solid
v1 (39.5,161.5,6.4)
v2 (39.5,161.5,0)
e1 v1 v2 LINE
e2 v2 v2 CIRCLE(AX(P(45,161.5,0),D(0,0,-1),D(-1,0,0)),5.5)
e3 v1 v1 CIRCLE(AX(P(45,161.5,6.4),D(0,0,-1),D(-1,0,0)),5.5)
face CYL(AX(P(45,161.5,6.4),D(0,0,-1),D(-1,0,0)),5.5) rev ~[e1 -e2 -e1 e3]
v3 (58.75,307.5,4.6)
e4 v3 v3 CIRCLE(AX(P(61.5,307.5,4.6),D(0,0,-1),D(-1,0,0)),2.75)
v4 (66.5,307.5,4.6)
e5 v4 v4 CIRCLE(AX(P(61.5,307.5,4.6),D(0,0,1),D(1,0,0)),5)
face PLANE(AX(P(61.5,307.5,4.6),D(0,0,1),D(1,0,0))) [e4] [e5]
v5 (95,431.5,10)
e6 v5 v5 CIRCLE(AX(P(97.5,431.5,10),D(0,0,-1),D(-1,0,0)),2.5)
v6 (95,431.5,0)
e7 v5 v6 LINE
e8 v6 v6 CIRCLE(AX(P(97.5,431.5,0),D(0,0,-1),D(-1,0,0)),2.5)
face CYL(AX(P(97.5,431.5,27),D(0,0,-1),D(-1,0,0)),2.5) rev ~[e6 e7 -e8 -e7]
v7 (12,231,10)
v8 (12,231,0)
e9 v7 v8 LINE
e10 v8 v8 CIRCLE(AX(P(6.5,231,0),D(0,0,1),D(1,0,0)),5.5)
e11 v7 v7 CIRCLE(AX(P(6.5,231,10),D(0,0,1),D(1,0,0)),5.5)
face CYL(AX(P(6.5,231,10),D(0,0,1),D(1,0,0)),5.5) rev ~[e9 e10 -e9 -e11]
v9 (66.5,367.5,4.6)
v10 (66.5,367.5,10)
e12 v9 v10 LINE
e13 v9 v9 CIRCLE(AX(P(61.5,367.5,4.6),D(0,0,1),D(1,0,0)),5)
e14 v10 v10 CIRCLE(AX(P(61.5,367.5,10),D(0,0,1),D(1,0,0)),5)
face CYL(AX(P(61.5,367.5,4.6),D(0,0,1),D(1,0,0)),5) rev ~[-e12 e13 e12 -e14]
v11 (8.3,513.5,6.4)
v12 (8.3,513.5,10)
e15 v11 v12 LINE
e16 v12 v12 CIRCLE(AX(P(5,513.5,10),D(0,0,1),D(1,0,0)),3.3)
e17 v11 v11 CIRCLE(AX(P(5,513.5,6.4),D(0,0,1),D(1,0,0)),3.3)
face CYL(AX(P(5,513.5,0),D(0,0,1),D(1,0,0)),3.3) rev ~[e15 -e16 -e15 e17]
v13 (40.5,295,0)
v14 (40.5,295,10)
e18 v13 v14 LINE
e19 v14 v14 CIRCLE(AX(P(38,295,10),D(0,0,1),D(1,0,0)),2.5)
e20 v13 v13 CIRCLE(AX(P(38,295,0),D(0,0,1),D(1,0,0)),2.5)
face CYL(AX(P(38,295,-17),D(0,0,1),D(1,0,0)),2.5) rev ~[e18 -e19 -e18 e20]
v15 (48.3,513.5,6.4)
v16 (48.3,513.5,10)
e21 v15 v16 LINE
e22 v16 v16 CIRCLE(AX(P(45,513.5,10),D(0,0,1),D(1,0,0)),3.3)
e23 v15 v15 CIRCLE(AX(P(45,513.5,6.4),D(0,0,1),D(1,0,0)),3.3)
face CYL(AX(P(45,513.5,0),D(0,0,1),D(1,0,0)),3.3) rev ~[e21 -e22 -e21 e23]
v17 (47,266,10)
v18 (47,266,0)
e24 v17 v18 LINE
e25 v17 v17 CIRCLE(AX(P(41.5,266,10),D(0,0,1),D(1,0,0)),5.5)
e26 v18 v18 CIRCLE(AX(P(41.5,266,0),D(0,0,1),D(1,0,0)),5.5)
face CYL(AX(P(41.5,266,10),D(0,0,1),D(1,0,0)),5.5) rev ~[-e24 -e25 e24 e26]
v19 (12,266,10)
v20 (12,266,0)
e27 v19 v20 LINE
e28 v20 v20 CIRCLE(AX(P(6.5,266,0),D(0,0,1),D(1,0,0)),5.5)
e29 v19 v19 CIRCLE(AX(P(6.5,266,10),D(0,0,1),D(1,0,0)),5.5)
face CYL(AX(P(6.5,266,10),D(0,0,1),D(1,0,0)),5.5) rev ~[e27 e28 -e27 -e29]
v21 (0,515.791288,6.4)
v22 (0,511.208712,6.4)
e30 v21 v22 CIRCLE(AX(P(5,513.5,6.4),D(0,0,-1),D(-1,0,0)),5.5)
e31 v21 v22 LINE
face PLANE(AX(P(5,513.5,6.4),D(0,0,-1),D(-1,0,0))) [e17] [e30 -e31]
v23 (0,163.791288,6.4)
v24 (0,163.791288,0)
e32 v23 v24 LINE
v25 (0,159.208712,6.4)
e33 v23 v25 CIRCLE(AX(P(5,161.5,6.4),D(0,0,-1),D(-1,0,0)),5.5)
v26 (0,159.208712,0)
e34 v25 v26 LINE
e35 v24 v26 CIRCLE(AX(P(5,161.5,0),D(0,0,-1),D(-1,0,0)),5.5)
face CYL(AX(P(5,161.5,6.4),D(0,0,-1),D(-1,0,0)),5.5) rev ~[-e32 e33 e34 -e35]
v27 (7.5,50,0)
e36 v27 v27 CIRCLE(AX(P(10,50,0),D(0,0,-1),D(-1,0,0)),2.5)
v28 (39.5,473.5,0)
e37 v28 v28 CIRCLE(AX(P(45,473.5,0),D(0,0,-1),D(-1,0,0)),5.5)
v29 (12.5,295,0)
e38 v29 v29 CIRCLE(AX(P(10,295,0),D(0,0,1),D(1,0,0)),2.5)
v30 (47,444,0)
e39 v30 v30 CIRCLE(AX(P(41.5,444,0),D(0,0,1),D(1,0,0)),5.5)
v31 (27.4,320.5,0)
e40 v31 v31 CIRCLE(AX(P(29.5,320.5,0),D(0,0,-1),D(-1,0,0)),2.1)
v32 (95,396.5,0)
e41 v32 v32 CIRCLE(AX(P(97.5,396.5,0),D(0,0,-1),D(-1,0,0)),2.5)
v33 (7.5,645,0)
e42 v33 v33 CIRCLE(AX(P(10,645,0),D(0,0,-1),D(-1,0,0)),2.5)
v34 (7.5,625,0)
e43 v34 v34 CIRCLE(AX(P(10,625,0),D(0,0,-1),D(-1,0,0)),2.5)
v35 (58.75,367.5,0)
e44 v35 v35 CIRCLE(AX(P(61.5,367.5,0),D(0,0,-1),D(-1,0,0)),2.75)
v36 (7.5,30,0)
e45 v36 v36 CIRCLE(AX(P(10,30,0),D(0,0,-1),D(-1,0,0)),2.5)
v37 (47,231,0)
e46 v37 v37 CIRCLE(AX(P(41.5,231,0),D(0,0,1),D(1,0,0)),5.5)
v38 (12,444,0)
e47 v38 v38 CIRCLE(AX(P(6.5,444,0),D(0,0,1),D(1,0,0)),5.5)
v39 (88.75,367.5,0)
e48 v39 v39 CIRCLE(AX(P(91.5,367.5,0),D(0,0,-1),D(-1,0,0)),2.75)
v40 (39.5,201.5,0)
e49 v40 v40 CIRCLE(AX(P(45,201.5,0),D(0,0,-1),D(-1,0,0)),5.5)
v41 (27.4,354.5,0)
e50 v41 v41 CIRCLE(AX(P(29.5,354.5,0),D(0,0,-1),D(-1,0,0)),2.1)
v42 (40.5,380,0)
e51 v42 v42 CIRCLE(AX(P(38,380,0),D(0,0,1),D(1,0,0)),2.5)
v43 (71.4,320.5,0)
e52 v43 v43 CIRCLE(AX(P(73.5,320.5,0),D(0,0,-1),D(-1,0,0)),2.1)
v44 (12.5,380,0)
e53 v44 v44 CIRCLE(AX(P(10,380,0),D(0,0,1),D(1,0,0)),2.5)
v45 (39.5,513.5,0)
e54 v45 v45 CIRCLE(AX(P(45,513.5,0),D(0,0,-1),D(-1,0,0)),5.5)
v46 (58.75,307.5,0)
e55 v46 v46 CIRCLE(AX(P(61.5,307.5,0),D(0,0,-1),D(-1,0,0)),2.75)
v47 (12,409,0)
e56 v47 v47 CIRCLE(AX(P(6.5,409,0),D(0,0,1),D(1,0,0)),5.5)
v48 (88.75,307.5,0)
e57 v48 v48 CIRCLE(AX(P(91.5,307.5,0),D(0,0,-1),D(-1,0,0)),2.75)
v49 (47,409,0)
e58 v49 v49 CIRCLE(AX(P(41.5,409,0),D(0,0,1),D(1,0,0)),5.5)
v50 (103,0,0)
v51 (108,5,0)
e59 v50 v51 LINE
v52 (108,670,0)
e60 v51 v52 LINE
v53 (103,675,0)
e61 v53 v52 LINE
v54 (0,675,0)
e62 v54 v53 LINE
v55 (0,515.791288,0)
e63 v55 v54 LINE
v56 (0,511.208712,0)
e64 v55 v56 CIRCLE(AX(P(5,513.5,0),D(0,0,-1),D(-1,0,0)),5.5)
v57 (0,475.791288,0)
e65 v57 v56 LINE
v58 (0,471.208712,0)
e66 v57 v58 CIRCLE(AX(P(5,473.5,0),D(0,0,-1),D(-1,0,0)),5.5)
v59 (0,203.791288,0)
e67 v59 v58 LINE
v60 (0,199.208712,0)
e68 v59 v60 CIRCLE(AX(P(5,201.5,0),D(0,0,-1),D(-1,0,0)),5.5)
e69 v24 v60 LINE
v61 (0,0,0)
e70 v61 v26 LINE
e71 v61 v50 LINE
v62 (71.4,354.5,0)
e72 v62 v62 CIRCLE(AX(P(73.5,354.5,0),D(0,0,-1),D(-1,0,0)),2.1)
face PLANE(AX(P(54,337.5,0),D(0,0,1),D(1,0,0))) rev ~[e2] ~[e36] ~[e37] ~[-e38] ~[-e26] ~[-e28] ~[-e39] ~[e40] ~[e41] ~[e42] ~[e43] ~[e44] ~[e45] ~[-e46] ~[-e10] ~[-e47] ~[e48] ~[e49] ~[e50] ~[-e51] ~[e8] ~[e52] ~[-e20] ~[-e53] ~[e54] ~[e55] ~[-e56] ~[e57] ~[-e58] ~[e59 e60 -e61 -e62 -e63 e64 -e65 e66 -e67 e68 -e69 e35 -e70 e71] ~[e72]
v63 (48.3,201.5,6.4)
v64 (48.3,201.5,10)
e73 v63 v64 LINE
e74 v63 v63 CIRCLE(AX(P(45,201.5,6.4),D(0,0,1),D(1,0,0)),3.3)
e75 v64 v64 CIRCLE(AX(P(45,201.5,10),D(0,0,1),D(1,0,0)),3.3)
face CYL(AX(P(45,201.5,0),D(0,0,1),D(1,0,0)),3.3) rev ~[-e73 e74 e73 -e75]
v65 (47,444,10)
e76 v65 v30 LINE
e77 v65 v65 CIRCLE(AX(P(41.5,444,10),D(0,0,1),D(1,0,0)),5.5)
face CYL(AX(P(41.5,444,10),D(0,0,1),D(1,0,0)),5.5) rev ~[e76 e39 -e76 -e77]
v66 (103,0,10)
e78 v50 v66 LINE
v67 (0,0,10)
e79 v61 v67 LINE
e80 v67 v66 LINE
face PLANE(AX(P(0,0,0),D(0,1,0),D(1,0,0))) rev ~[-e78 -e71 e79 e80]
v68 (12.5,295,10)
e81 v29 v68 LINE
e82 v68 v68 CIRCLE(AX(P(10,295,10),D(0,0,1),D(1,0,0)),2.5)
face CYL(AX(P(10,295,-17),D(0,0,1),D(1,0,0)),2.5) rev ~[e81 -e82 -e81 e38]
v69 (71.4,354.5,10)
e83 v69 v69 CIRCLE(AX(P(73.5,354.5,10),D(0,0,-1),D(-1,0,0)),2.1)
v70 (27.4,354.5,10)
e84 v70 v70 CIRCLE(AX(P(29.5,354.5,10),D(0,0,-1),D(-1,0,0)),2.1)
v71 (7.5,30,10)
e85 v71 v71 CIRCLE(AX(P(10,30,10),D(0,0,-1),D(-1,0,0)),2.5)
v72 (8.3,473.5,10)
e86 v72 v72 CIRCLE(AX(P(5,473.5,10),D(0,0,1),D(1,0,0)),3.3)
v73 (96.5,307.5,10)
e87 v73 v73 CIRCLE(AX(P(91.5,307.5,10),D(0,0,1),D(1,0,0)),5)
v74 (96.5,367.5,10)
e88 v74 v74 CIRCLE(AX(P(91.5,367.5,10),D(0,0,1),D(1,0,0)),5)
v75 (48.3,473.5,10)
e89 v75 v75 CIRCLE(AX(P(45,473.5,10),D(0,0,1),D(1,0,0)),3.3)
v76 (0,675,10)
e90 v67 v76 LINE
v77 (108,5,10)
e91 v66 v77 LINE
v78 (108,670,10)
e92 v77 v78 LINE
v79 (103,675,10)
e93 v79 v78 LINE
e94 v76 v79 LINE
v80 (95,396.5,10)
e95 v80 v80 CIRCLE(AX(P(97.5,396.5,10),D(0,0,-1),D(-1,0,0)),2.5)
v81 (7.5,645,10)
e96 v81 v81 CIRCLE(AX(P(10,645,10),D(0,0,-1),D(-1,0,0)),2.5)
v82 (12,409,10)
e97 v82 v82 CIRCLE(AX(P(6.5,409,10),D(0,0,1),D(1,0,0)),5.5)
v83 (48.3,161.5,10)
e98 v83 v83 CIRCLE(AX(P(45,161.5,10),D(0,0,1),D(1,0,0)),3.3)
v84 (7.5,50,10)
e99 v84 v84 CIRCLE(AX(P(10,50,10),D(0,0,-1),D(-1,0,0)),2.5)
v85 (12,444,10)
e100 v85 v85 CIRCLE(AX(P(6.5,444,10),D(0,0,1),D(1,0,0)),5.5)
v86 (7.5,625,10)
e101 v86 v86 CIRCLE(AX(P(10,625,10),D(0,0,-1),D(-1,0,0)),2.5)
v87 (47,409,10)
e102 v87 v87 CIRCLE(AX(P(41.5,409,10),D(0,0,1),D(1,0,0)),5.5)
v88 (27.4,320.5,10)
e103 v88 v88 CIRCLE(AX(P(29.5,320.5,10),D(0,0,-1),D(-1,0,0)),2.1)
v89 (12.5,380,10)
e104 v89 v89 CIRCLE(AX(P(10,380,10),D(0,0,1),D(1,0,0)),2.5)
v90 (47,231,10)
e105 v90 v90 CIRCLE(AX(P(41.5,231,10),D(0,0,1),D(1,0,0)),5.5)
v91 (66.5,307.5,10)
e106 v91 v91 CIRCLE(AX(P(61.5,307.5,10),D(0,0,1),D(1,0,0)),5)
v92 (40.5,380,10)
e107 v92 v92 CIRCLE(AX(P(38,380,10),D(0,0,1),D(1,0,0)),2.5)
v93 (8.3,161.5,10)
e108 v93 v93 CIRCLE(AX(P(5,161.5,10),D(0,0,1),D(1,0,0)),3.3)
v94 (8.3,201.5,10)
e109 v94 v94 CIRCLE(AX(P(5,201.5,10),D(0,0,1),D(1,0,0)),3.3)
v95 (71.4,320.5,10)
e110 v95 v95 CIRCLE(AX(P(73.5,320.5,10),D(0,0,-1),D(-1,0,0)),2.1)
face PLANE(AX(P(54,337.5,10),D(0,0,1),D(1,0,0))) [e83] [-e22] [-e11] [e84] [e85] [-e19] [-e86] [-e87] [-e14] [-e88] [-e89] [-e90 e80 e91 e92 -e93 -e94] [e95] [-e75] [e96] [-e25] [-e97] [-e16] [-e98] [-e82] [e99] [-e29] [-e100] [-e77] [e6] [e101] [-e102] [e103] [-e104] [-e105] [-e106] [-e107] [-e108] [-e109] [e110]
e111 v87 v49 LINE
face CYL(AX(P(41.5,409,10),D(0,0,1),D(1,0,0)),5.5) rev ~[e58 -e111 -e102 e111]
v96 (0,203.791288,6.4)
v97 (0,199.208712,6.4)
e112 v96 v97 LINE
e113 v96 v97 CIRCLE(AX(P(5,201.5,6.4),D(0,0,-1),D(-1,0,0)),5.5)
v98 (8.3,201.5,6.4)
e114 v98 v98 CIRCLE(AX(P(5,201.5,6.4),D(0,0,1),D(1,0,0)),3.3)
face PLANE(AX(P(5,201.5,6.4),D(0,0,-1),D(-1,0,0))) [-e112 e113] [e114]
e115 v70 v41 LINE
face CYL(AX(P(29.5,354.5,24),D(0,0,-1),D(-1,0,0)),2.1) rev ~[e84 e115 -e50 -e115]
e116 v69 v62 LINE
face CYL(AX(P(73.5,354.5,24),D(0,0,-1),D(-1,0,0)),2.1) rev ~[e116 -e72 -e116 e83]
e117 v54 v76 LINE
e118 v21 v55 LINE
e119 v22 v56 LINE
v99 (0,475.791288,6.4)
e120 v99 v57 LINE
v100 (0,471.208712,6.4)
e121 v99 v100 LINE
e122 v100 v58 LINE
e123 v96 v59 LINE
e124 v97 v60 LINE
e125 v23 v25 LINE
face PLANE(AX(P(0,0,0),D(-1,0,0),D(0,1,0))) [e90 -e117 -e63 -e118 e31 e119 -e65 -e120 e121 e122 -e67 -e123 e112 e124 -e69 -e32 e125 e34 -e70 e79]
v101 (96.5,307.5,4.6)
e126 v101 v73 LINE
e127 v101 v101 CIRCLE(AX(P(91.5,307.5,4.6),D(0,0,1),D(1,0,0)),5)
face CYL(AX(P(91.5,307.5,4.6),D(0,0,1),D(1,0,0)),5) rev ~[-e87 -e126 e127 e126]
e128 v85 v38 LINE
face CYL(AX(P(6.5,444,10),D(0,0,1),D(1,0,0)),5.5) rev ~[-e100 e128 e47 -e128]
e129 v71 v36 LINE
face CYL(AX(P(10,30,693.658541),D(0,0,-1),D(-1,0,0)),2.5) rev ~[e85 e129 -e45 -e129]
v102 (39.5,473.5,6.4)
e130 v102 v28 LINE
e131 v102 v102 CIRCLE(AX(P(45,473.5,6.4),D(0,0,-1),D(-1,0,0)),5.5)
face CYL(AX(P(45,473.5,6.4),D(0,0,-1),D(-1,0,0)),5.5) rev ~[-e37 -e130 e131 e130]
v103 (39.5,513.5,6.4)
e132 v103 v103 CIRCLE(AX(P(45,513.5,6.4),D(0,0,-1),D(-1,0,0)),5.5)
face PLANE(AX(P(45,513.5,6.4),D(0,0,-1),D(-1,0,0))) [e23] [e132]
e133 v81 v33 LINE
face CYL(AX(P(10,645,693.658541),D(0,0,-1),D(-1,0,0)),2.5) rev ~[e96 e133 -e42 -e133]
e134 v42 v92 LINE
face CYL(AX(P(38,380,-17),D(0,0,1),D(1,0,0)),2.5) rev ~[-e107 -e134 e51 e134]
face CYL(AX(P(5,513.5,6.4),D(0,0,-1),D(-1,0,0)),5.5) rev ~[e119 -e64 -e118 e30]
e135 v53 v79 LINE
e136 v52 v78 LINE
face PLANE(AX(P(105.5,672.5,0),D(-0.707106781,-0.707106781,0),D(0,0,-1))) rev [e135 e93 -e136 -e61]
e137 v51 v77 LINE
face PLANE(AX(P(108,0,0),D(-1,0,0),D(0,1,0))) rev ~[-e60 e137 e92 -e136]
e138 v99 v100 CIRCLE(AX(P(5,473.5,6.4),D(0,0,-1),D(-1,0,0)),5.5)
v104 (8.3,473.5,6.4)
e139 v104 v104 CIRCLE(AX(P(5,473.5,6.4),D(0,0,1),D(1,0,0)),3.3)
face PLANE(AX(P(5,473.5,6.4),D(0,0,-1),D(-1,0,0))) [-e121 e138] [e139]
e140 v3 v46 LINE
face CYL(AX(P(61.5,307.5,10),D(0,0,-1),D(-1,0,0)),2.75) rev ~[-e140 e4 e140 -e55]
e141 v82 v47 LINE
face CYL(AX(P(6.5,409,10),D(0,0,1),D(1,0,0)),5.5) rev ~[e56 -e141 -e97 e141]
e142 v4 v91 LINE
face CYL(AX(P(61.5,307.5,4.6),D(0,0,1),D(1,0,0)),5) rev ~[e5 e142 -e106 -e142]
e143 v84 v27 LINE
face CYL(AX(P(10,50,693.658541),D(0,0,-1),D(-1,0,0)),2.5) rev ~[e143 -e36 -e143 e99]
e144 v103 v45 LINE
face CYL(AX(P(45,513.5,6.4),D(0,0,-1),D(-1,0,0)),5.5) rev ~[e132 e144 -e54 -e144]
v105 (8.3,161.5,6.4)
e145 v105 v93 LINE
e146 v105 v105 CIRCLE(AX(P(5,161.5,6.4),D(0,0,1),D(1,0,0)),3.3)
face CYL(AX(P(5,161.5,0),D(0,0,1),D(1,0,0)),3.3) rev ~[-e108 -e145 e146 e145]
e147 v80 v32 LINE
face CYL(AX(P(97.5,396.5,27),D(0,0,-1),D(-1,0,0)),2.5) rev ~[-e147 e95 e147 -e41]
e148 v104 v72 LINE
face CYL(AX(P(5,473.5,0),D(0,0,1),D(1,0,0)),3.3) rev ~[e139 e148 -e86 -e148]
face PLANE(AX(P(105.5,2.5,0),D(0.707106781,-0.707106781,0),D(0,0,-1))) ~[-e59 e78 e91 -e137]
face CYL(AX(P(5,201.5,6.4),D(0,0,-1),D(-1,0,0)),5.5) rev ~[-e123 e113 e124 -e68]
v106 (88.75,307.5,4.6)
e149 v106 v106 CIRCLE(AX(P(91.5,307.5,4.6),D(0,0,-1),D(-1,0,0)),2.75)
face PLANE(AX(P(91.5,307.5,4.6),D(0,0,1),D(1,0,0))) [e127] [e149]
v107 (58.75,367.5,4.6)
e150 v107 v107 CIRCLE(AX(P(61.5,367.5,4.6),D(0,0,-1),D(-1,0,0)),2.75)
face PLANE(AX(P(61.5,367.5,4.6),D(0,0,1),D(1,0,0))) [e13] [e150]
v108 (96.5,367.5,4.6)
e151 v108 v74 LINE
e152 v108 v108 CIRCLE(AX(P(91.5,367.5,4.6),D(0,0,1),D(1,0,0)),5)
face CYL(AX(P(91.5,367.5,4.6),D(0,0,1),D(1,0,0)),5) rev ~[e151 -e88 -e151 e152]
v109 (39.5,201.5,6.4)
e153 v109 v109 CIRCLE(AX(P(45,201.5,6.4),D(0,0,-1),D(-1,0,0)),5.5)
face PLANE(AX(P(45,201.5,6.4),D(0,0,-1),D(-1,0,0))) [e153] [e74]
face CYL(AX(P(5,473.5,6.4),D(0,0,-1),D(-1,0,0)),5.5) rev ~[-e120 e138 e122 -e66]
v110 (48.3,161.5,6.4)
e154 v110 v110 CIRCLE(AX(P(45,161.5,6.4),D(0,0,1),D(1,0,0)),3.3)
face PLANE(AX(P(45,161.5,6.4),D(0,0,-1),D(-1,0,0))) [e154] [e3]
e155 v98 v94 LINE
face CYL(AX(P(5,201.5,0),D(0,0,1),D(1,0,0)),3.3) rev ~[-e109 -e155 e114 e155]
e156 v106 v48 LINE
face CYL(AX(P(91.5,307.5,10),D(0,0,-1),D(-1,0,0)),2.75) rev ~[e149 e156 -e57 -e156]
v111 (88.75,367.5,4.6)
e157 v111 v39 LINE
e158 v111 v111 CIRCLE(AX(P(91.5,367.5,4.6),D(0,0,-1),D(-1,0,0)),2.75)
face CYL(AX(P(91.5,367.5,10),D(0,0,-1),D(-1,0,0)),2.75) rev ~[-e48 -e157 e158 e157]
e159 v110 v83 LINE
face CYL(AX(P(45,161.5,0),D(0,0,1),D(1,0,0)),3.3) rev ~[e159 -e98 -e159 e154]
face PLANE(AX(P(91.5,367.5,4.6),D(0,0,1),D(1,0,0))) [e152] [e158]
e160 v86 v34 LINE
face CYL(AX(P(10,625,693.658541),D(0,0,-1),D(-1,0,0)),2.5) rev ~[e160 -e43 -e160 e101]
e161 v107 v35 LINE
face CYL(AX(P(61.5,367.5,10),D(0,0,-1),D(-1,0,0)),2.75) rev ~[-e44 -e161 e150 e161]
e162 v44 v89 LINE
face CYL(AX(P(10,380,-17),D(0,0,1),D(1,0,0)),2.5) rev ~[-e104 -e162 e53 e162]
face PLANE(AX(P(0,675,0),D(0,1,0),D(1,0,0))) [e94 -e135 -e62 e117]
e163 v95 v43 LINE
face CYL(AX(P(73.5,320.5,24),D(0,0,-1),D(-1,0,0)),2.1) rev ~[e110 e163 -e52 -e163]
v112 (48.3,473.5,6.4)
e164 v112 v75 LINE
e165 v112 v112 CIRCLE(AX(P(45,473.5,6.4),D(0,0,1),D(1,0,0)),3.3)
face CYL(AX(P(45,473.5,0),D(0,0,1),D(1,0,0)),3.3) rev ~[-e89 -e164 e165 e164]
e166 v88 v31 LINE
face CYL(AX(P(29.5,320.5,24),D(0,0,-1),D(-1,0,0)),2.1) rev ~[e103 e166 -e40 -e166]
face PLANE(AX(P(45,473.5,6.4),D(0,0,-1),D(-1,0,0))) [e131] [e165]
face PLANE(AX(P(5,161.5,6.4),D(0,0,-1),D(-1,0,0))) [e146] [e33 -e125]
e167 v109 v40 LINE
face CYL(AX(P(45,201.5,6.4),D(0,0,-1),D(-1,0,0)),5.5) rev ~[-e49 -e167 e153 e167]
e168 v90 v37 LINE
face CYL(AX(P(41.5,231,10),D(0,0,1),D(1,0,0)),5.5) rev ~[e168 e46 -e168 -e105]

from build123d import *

# Parameters (mm, degrees)
SKETCH_1_W                     = 108
SKETCH_1_H                     = 675
EXTRUDE_1_DEPTH                = 10
HOLE_WIZARD_M6_1_D             = 5
HOLE_WIZARD_M6_1_2_D           = 6.6
HOLE_WIZARD_M6_1_2_CBORE_D     = 11
HOLE_WIZARD_M6_1_2_CBORE_DEPTH = 6.4
HOLE_WIZARD_M5_1_D             = 4.2
HOLE_WIZARD_M5_1_DEPTH         = 14
HOLE_WIZARD_M5_1_TIP           = 1.2618073
HOLE_WIZARD_M6_2_D             = 5
HOLE_WIZARD_M6_2_DEPTH         = 17
HOLE_WIZARD_M6_2_TIP           = 1.502151548
HOLE_WIZARD_M5_1_2_D           = 5.5
HOLE_WIZARD_M5_1_2_DEPTH       = 14
HOLE_WIZARD_M5_1_2_CBORE_D     = 10
HOLE_WIZARD_M5_1_2_CBORE_DEPTH = 5.4
HOLE_WIZARD_M5_1_2_TIP         = 1.652366702
HOLE_WIZARD_M6_3_D             = 5
HOLE_WIZARD_M6_3_DEPTH         = 17
HOLE_WIZARD_M6_3_TIP           = 1.502151548
SKETCH_14_R                    = 5.5
CUT_EXTRUDE_1_DEPTH            = 60
CHAMFER_1_SIZE                 = 5


with BuildPart() as part:
    # 草图1 → 凸台-拉伸1 (new body)
    with BuildSketch(Plane.XY):
        with Locations((54, 337.5)):
            Rectangle(SKETCH_1_W, SKETCH_1_H)
    extrude(amount=EXTRUDE_1_DEPTH)

    # Hole Wizard M6 _1 (through all)
    with Locations(Plane.XY.offset(10)):
        with Locations((10, 645), (10, 625), (10, 50), (10, 30)):
            Hole(HOLE_WIZARD_M6_1_D / 2)

    # Hole Wizard M6 _1 2 (through all)
    with Locations(Plane(origin=(0, 0, 0), x_dir=(-1, 0, 0), z_dir=(0, 0, -1))):
        with Locations((-45, 513.5), (-5, 513.5), (-45, 473.5), (-5, 473.5), (-5, 201.5), (-45, 201.5), (-5, 161.5), (-45, 161.5)):
            CounterBoreHole(HOLE_WIZARD_M6_1_2_D / 2, HOLE_WIZARD_M6_1_2_CBORE_D / 2, HOLE_WIZARD_M6_1_2_CBORE_DEPTH)

    # Hole Wizard M5 _1
    with Locations(Plane.XY.offset(10)):
        with Locations((29.5, 354.5), (73.5, 354.5), (29.5, 320.5), (73.5, 320.5)):
            Hole(HOLE_WIZARD_M5_1_D / 2, depth=HOLE_WIZARD_M5_1_DEPTH)
            with Locations((0, 0, -(HOLE_WIZARD_M5_1_DEPTH + HOLE_WIZARD_M5_1_TIP / 2))):  # 118° drill point
                Cone(0, HOLE_WIZARD_M5_1_D / 2, HOLE_WIZARD_M5_1_TIP, mode=Mode.SUBTRACT)

    # M6 螺纹孔2
    with Locations(Plane.XY.offset(10)):
        with Locations((97.5, 431.5), (97.5, 396.5)):
            Hole(HOLE_WIZARD_M6_2_D / 2, depth=HOLE_WIZARD_M6_2_DEPTH)
            with Locations((0, 0, -(HOLE_WIZARD_M6_2_DEPTH + HOLE_WIZARD_M6_2_TIP / 2))):  # 118° drill point
                Cone(0, HOLE_WIZARD_M6_2_D / 2, HOLE_WIZARD_M6_2_TIP, mode=Mode.SUBTRACT)

    # Hole Wizard M5 _1 2
    with Locations(Plane.XY.offset(10)):
        with Locations((61.5, 367.5), (91.5, 367.5), (61.5, 307.5), (91.5, 307.5)):
            CounterBoreHole(HOLE_WIZARD_M5_1_2_D / 2, HOLE_WIZARD_M5_1_2_CBORE_D / 2, HOLE_WIZARD_M5_1_2_CBORE_DEPTH, depth=HOLE_WIZARD_M5_1_2_DEPTH)
            with Locations((0, 0, -(HOLE_WIZARD_M5_1_2_DEPTH + HOLE_WIZARD_M5_1_2_TIP / 2))):  # 118° drill point
                Cone(0, HOLE_WIZARD_M5_1_2_D / 2, HOLE_WIZARD_M5_1_2_TIP, mode=Mode.SUBTRACT)

    # M6 螺纹孔3
    with Locations(Plane(origin=(0, 0, 0), x_dir=(-1, 0, 0), z_dir=(0, 0, -1))):
        with Locations((-38, 380), (-10, 380), (-38, 295), (-10, 295)):
            Hole(HOLE_WIZARD_M6_3_D / 2, depth=HOLE_WIZARD_M6_3_DEPTH)
            with Locations((0, 0, -(HOLE_WIZARD_M6_3_DEPTH + HOLE_WIZARD_M6_3_TIP / 2))):  # 118° drill point
                Cone(0, HOLE_WIZARD_M6_3_D / 2, HOLE_WIZARD_M6_3_TIP, mode=Mode.SUBTRACT)

    # 草图14 → 切除-拉伸1 (cut)
    with BuildSketch(Plane.XY.offset(10)):
        with Locations((41.5, 444)):
            Circle(SKETCH_14_R)
        with Locations((6.5, 444)):
            Circle(SKETCH_14_R)
        with Locations((41.5, 409)):
            Circle(SKETCH_14_R)
        with Locations((6.5, 409)):
            Circle(SKETCH_14_R)
        with Locations((41.5, 266)):
            Circle(SKETCH_14_R)
        with Locations((41.5, 231)):
            Circle(SKETCH_14_R)
        with Locations((6.5, 231)):
            Circle(SKETCH_14_R)
        with Locations((6.5, 266)):
            Circle(SKETCH_14_R)
    extrude(amount=-CUT_EXTRUDE_1_DEPTH, mode=Mode.SUBTRACT)

    # 倒角1
    chamfer_1_edges = [part.edges().sort_by_distance(p)[0] for p in [
        (108, 0, 5),
        (108, 675, 5),
    ]]
    chamfer(chamfer_1_edges, length=CHAMFER_1_SIZE)


solid = part.part
